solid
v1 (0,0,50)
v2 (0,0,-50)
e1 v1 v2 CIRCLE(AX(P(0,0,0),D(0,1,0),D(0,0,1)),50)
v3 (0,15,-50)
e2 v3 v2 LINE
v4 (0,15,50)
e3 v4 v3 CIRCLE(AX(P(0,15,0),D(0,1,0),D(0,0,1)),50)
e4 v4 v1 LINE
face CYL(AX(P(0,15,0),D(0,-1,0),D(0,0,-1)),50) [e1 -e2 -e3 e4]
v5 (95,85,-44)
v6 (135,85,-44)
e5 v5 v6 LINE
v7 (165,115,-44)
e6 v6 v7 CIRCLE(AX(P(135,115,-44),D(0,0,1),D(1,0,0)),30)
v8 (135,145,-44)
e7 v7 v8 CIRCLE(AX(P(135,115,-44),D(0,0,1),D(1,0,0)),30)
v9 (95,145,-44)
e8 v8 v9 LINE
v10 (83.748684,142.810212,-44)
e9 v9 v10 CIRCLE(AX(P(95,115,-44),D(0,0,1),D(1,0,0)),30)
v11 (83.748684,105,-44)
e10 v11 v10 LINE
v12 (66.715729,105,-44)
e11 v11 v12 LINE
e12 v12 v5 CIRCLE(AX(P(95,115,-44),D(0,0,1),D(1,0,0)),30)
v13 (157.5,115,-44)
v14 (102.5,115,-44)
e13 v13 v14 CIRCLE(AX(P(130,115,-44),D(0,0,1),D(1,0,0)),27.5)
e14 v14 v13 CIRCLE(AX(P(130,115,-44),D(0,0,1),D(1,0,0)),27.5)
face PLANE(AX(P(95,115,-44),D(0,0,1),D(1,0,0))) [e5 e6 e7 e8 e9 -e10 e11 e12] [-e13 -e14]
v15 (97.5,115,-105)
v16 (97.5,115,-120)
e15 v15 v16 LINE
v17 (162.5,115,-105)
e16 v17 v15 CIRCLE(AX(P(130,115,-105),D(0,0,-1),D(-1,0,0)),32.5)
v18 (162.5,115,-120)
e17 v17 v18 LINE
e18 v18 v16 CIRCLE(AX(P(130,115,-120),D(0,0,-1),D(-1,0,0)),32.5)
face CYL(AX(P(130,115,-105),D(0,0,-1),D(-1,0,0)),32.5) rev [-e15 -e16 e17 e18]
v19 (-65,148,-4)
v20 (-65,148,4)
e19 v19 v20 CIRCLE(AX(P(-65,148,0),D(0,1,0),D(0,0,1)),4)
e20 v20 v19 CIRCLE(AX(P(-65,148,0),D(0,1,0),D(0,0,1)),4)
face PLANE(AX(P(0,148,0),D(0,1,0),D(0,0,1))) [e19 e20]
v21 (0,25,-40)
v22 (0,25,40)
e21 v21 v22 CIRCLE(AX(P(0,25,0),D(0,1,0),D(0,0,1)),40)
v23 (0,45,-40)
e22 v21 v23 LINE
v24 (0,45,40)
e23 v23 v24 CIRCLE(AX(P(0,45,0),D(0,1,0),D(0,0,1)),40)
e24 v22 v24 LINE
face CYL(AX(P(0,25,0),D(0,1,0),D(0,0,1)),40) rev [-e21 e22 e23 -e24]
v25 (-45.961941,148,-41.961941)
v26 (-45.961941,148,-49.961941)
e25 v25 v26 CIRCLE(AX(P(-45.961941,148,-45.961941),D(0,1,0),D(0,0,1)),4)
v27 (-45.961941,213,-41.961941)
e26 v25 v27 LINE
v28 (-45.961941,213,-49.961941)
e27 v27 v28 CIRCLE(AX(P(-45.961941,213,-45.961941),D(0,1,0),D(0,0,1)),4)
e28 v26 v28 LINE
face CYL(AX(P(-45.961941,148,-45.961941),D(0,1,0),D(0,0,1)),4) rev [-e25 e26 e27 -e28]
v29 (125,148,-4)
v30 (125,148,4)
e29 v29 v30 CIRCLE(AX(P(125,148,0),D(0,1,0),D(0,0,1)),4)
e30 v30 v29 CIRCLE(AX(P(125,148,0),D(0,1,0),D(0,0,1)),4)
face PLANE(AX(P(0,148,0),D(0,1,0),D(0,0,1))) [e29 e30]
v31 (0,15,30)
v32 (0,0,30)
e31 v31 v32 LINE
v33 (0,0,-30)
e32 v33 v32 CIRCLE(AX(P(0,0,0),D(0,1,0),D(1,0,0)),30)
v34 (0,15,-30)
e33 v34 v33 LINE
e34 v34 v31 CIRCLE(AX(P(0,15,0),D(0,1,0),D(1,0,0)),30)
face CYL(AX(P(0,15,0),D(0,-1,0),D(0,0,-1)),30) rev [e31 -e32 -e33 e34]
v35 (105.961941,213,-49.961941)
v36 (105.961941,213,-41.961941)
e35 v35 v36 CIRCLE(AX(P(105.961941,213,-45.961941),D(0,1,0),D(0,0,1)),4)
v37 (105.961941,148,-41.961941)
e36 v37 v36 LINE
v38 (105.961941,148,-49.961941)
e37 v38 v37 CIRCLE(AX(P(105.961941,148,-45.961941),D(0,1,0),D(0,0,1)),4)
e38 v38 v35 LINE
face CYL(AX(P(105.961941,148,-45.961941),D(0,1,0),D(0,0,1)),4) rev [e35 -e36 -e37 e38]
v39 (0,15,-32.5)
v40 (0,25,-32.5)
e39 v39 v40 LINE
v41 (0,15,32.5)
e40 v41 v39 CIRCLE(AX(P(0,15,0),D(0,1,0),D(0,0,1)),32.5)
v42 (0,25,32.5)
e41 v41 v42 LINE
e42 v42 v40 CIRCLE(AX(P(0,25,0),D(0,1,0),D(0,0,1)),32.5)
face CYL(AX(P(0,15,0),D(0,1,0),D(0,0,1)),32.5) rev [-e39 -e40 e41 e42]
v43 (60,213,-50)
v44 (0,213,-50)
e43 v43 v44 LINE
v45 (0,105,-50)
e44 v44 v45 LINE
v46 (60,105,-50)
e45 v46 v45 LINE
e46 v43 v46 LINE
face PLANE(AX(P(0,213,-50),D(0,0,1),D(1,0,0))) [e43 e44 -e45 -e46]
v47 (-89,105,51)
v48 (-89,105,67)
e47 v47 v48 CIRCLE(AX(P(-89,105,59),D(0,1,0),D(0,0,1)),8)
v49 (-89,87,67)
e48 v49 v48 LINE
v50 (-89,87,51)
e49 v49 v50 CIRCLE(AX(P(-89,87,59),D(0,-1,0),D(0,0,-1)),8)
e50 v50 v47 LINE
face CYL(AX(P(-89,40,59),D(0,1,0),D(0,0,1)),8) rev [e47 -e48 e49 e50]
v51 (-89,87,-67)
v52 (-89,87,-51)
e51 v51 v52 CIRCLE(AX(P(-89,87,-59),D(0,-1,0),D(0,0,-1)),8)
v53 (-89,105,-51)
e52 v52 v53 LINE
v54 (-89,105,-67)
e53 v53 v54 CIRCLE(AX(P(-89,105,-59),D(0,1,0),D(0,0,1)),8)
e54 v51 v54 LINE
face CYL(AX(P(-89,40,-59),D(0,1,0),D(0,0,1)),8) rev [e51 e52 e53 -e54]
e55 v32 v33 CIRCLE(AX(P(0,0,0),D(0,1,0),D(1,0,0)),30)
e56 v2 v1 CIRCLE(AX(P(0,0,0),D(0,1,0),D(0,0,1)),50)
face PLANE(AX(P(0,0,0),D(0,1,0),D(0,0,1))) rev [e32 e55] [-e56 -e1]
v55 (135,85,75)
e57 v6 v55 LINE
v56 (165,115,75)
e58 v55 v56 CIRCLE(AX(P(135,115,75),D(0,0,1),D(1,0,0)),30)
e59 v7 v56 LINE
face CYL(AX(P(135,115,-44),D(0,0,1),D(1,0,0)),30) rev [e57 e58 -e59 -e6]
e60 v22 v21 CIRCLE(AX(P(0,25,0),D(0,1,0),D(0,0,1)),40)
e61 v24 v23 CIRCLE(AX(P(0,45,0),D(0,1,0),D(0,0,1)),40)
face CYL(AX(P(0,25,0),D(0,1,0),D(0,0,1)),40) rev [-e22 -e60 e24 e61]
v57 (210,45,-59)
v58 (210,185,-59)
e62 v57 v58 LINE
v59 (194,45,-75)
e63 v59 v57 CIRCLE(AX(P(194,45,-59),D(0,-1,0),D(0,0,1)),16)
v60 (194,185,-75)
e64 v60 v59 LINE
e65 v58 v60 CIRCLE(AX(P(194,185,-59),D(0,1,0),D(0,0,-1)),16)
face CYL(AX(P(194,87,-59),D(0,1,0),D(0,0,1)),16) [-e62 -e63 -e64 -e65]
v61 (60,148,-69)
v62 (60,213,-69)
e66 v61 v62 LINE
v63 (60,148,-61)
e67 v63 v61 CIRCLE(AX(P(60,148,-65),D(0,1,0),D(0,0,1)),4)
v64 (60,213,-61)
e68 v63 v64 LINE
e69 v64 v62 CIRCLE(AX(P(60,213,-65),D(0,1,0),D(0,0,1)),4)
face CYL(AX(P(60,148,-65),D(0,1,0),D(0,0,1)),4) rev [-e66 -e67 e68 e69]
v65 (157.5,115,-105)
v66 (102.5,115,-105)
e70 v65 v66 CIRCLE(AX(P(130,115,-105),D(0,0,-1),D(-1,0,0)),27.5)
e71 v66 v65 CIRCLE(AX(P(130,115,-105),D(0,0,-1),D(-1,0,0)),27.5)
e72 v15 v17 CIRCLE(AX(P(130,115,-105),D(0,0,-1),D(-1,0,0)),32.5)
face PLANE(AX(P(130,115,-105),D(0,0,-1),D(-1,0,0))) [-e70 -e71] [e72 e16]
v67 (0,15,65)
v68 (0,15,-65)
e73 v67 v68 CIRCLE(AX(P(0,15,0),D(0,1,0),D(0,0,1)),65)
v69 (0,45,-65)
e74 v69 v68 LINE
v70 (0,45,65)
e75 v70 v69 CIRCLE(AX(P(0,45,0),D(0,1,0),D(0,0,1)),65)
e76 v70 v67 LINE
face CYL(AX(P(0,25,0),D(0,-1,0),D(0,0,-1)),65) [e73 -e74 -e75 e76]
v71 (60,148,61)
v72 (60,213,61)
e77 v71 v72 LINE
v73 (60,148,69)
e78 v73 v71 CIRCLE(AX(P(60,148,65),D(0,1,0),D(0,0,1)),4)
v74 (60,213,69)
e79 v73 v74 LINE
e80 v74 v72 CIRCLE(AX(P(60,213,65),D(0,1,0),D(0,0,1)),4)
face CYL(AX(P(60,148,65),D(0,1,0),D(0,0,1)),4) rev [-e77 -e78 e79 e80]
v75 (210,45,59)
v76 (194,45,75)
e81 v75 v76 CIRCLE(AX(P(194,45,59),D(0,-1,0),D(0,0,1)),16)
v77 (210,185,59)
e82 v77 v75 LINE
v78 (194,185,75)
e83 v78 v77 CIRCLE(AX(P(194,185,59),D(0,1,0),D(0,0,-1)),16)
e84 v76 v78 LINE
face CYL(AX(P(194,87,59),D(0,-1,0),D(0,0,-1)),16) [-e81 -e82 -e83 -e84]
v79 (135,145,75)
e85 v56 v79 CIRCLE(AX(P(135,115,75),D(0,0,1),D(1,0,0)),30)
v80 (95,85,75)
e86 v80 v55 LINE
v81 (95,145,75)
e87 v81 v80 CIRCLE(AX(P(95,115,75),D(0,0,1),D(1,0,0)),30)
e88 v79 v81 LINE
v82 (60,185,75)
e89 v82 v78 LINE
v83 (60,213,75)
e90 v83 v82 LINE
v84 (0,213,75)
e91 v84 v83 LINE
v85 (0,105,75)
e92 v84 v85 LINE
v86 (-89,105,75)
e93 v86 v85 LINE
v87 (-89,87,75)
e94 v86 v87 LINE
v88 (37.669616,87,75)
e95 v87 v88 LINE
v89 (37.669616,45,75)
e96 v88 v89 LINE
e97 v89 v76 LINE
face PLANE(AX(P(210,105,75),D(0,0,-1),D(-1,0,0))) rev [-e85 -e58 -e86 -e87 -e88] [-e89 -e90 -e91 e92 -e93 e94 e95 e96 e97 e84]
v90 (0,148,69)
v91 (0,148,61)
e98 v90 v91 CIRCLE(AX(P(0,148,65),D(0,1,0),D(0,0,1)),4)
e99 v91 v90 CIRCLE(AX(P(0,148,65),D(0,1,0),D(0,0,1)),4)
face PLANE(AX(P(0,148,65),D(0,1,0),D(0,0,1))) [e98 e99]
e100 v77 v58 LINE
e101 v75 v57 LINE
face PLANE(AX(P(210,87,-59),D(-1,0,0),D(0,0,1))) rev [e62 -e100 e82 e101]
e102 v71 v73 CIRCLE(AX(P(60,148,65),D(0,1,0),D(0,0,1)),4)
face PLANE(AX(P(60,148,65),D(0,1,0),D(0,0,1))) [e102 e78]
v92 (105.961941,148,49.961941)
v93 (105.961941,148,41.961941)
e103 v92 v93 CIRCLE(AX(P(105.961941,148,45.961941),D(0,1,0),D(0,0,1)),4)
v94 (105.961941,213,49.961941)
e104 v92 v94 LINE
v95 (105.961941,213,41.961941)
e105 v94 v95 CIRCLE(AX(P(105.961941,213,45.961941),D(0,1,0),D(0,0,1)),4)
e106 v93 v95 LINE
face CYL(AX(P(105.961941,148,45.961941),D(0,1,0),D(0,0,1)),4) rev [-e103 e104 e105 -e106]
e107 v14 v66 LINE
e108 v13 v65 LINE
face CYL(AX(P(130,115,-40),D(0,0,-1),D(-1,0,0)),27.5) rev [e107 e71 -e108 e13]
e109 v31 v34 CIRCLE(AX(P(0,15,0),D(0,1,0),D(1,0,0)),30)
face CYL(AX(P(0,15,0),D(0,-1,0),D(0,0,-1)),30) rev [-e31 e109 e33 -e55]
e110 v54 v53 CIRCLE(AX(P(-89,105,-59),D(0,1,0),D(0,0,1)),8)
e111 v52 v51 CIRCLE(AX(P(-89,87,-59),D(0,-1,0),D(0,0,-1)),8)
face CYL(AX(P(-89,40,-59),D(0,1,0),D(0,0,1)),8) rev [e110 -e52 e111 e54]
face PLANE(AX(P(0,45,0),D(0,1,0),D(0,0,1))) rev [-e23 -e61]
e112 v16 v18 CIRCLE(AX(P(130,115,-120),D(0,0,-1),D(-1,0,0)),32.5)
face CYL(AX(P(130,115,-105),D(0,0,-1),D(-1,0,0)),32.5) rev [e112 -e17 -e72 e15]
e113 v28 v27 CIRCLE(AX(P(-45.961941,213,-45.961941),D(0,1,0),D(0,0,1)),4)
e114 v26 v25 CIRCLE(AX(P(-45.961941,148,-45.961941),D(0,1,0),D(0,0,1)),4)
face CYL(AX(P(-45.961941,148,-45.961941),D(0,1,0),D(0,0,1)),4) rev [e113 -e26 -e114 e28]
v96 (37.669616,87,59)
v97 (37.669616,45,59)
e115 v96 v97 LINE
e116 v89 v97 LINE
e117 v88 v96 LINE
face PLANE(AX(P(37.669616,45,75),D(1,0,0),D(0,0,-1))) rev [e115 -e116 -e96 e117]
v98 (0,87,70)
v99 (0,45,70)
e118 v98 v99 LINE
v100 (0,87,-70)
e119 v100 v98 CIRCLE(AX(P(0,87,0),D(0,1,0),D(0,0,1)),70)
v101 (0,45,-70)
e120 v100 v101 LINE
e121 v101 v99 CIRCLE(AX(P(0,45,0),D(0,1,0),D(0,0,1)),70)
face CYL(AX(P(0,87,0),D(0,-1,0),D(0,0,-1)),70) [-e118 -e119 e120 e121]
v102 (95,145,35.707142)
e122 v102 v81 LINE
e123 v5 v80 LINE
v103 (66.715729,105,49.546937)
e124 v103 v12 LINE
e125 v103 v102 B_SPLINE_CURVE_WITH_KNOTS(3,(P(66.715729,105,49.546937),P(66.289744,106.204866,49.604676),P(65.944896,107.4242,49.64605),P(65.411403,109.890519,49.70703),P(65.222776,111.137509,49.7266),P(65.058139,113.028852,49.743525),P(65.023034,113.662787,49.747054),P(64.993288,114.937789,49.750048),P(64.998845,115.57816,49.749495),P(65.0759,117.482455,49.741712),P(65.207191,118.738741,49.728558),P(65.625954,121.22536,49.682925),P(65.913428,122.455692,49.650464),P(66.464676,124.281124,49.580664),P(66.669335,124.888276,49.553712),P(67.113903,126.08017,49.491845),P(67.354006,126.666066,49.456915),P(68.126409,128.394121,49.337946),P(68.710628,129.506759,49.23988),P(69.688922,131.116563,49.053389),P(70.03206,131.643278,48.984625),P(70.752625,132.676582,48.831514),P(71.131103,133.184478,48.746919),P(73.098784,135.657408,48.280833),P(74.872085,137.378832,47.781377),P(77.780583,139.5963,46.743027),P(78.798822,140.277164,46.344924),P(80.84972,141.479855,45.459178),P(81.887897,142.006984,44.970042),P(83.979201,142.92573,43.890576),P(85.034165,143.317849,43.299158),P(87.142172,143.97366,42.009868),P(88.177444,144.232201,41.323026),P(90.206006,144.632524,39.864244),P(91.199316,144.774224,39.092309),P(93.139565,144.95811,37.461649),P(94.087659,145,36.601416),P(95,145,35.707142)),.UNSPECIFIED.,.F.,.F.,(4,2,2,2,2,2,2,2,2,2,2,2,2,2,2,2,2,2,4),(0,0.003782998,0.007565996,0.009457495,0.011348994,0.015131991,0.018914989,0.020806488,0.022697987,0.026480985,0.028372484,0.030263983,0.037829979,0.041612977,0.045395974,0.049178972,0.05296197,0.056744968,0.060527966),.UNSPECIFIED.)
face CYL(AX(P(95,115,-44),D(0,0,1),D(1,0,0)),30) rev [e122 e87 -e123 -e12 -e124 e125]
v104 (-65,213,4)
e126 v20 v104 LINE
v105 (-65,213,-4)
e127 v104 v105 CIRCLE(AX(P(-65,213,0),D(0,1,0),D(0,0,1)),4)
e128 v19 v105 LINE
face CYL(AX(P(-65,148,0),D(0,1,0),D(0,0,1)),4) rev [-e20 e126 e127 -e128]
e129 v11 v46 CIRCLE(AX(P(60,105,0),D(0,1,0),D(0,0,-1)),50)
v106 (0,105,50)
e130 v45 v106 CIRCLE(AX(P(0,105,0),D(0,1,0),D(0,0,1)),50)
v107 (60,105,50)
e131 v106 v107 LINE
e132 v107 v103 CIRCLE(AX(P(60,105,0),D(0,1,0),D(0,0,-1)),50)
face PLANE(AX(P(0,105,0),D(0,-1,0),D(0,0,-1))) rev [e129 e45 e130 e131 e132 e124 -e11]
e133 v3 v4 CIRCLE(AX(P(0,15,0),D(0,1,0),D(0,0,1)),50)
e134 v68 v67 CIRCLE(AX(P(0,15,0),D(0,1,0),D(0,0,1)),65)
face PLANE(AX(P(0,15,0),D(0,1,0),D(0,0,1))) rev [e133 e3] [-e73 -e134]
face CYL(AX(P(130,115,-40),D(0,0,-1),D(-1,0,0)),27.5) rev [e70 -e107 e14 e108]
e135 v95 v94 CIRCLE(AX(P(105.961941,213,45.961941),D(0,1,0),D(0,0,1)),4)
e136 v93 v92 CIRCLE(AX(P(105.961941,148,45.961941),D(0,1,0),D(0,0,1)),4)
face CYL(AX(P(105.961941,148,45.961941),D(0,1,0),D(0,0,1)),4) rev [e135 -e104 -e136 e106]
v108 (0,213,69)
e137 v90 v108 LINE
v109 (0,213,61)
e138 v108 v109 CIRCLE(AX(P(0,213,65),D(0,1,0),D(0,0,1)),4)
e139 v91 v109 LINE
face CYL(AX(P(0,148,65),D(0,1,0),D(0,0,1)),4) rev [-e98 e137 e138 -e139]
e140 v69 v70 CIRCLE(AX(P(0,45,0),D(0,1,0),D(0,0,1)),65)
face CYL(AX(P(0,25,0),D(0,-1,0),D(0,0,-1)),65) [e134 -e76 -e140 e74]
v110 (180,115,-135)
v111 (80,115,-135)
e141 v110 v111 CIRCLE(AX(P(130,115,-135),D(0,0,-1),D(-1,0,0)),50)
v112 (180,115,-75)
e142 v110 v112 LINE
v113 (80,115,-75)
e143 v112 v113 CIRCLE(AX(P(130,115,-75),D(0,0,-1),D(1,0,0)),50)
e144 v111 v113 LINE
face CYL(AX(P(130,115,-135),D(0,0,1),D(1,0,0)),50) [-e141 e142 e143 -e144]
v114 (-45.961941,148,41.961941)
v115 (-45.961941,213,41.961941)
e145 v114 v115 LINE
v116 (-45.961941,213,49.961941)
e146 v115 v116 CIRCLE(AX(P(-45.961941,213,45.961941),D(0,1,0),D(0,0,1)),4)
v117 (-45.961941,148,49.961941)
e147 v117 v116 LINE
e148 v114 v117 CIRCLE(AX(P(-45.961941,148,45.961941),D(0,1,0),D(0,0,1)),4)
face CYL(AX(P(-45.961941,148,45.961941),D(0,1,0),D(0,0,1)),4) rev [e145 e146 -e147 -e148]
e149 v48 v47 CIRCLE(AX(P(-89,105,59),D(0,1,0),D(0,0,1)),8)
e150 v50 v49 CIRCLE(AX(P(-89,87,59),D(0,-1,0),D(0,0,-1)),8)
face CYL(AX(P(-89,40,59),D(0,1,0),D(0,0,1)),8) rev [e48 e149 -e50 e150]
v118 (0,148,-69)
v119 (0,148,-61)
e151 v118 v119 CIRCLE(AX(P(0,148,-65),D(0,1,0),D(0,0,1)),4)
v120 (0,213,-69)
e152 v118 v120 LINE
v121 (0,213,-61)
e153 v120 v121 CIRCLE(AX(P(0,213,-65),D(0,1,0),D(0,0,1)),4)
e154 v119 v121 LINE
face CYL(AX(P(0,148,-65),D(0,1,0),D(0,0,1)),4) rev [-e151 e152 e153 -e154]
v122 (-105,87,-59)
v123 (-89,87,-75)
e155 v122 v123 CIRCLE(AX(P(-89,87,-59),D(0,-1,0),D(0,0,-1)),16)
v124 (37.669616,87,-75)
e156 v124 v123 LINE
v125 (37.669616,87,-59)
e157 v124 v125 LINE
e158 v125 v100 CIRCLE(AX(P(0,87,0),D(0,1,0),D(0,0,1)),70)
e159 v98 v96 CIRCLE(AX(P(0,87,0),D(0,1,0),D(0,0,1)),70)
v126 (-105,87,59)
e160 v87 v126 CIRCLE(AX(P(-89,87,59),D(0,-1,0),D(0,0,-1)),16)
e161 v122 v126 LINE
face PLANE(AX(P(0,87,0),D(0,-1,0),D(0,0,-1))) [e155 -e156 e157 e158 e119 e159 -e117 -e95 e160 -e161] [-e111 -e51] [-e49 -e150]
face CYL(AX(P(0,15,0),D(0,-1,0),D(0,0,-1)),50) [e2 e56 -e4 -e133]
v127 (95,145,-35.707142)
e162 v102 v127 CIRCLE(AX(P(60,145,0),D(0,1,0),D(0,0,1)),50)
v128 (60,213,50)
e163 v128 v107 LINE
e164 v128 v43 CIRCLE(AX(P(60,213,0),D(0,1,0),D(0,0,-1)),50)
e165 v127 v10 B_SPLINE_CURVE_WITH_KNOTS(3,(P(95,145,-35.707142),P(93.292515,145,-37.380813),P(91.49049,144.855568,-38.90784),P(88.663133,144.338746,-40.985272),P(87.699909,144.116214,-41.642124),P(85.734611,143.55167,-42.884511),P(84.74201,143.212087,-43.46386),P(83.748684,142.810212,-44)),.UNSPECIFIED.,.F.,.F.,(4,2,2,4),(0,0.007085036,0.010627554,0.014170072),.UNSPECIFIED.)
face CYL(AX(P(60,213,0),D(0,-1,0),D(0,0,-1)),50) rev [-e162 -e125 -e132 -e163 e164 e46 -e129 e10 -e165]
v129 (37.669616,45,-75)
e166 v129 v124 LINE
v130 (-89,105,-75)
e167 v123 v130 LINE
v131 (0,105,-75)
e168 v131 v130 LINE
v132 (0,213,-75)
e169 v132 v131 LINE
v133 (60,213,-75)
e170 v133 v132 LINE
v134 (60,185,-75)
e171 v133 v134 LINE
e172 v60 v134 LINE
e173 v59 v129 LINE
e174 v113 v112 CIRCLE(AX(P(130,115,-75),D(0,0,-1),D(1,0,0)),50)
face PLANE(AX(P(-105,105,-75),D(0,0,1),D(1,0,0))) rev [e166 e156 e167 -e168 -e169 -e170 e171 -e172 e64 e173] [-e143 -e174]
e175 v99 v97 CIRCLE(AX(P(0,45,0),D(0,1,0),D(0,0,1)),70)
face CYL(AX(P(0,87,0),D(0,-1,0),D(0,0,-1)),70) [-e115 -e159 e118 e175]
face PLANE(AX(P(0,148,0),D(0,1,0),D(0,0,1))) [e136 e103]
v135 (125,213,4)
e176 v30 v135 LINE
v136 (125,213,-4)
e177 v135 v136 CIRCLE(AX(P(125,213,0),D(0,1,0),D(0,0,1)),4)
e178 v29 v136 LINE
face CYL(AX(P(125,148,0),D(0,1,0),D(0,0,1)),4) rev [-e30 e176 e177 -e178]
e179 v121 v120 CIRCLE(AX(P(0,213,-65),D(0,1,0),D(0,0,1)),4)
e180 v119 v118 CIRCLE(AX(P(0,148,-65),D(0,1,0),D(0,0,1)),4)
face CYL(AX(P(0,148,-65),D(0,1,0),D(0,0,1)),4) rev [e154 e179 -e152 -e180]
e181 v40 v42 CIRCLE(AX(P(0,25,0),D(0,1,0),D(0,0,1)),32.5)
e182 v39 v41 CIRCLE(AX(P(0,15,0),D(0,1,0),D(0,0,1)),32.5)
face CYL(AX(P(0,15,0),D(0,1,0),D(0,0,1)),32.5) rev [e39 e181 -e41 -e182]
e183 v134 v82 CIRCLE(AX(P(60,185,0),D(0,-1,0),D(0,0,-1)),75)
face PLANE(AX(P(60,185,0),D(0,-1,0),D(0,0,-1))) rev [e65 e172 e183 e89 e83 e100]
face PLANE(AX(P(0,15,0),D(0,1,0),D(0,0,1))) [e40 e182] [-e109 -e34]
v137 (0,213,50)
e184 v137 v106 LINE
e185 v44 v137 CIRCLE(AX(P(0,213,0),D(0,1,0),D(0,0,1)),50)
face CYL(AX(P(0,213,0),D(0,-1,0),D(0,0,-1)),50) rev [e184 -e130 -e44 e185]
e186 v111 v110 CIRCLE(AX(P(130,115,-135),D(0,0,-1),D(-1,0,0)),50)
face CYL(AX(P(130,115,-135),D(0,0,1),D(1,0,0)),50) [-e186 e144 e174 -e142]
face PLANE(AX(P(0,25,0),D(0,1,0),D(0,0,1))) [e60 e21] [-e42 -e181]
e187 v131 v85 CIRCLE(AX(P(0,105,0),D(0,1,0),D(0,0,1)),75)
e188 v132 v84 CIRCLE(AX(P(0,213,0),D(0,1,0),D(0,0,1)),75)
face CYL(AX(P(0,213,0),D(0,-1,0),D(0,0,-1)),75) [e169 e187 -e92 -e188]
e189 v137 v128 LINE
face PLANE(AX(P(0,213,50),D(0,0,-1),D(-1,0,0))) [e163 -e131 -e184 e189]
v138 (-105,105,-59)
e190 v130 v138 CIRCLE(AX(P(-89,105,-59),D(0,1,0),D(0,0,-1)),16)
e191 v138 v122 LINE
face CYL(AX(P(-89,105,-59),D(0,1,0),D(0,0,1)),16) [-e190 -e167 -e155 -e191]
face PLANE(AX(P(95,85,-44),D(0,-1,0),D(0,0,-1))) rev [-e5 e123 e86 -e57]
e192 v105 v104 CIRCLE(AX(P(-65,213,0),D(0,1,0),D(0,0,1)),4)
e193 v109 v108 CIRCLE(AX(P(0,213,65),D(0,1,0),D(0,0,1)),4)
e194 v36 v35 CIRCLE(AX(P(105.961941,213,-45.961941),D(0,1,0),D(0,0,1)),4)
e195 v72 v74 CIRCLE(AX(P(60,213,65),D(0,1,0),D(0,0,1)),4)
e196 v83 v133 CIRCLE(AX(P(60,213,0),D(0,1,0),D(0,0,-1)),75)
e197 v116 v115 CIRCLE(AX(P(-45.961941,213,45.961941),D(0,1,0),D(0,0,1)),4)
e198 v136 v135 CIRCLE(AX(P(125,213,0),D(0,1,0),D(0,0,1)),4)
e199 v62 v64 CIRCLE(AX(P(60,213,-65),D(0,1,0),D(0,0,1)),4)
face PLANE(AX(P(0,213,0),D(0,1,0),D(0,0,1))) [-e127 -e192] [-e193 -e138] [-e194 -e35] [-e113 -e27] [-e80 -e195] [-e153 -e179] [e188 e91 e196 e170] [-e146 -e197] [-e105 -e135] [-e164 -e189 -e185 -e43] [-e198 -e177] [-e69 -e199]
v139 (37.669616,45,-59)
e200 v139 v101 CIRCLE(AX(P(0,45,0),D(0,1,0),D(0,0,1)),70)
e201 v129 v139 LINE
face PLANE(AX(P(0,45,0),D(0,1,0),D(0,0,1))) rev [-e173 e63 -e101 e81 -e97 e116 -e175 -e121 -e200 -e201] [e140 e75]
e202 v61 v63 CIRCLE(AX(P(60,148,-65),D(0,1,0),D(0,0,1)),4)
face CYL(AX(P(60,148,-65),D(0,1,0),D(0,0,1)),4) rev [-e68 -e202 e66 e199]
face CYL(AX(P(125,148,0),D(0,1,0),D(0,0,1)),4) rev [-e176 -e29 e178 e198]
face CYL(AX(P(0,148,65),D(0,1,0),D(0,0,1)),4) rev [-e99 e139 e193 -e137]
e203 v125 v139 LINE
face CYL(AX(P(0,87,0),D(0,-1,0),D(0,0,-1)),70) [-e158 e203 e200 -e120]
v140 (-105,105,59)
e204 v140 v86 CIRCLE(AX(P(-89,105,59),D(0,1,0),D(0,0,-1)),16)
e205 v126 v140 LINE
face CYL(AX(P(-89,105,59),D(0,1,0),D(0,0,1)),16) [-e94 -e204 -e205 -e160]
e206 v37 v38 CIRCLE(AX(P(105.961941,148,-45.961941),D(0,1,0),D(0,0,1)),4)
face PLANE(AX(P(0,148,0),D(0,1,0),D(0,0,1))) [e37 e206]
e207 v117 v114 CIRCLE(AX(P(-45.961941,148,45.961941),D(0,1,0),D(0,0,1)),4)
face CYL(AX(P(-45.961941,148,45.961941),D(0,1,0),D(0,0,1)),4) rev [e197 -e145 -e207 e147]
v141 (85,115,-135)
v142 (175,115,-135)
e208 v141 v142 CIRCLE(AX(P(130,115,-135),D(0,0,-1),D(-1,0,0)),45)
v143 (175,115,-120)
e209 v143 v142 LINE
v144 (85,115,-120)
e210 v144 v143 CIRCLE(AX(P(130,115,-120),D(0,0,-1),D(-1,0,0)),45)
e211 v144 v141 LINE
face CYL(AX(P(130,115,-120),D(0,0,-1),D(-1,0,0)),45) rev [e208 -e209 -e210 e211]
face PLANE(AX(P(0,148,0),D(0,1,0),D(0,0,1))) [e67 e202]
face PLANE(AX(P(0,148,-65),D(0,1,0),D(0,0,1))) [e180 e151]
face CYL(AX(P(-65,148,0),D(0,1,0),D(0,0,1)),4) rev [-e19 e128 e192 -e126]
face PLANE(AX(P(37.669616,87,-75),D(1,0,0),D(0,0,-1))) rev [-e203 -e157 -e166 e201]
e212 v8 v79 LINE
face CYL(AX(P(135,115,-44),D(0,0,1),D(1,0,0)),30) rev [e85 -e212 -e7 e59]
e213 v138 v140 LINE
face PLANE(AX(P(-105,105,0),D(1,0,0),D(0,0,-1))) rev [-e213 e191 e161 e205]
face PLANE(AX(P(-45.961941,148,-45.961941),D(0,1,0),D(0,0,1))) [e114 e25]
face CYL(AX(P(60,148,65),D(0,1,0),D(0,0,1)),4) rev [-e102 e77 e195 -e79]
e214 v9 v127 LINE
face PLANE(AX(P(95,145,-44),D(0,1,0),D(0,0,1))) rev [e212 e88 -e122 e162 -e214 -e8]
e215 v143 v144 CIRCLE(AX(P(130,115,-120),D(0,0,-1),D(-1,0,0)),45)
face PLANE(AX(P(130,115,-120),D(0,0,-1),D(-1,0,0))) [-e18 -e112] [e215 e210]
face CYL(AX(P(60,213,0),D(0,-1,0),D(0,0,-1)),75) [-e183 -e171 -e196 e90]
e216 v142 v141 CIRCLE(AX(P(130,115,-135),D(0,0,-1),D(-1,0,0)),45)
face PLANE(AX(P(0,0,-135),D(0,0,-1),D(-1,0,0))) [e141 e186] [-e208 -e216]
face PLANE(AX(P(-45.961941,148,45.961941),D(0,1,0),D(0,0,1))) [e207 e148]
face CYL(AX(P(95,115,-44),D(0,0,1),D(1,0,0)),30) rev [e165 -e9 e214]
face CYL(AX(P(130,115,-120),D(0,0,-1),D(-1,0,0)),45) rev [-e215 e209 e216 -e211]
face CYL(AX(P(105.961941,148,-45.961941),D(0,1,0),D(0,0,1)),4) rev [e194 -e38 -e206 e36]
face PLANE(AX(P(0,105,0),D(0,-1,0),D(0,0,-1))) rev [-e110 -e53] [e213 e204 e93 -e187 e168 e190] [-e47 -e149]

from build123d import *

# Parameters (mm, degrees)
BASE_TUBE_SKETCH_R                 = 50
BASE_TUBE_SKETCH_R_2               = 30
BASE_TUBE_DEPTH                    = 15
LOWER_FLANGE_SKETCH_R              = 65
LOWER_FLANGE_DEPTH                 = 10
LOWER_FLANGE_BORE_SKETCH_R         = 32.5
LOWER_FLANGE_BORE_DEPTH            = 10
SPIGOT_SKETCH_R                    = 65
SPIGOT_DEPTH                       = 20
SPIGOT_BORE_SKETCH_R               = 40
SPIGOT_BORE_DEPTH                  = 20
LOWER_BLOCK_DEPTH                  = 42
MOUNTING_LUG_DEPTH                 = 18
MAIN_BODY_DEPTH                    = 108
BODY_EXTENSION_DEPTH               = 80
INFILL_BLOCK_A_SKETCH_W            = 172.330383596
INFILL_BLOCK_A_SKETCH_H            = 42
INFILL_BLOCK_A_DEPTH               = 16
THROUGH_SLOT_DEPTH                 = 119
INFILL_BLOCK_B_SKETCH_W            = 172.330383596
INFILL_BLOCK_B_SKETCH_H            = 42
INFILL_BLOCK_B_DEPTH               = 16
SIDE_PORT_BOSS_SKETCH_R            = 50
SIDE_PORT_BOSS_DEPTH               = 60
PORT_COUNTERBORE_SKETCH_R          = 45
PORT_COUNTERBORE_DEPTH             = 15
PORT_STEP_BORE_SKETCH_R            = 32.5
PORT_STEP_BORE_DEPTH               = 15
PORT_THROUGH_BORE_SKETCH_R         = 27.5
PORT_THROUGH_BORE_DEPTH            = 65
BLOCK_EDGE_FILLET_R16_A_R          = 16
BLOCK_EDGE_FILLET_R16_B_R          = 16
LUG_EDGE_FILLET_R16_A_R            = 16
LUG_EDGE_FILLET_R16_B_R            = 16
LUG_POCKET_SKETCH_R                = 8
LUG_POCKET_DEPTH                   = 65
TOP_CAVITY_AND_BOLT_HOLES_SKETCH_R = 4
TOP_CAVITY_AND_BOLT_HOLES_DEPTH    = 65


with BuildPart() as part:
    # Base Tube Sketch → Base Tube (new body)
    with BuildSketch(Plane(origin=(0, 0, 0), x_dir=(1, 0, 0), z_dir=(0, 1, 0))):
        Circle(BASE_TUBE_SKETCH_R)
        Circle(BASE_TUBE_SKETCH_R_2, mode=Mode.SUBTRACT)
    extrude(amount=BASE_TUBE_DEPTH)

    # Lower Flange Sketch → Lower Flange (add)
    with BuildSketch(Plane(origin=(0, 15, 0), x_dir=(1, 0, 0), z_dir=(0, 1, 0))):
        with Locations(Location((0, 0, 0), (0, 0, 270))):
            Circle(LOWER_FLANGE_SKETCH_R)
    extrude(amount=LOWER_FLANGE_DEPTH)

    # Lower Flange Bore Sketch → Lower Flange Bore (cut)
    with BuildSketch(Plane(origin=(0, 25, 0), x_dir=(1, 0, 0), z_dir=(0, 1, 0))):
        with Locations(Location((0, 0, 0), (0, 0, 270))):
            Circle(LOWER_FLANGE_BORE_SKETCH_R)
    extrude(amount=-LOWER_FLANGE_BORE_DEPTH, mode=Mode.SUBTRACT)

    # Spigot Sketch → Spigot (add)
    with BuildSketch(Plane(origin=(0, 25, 0), x_dir=(1, 0, 0), z_dir=(0, 1, 0))):
        with Locations(Location((0, 0, 0), (0, 0, 270))):
            Circle(SPIGOT_SKETCH_R)
    extrude(amount=SPIGOT_DEPTH)

    # Spigot Bore Sketch → Spigot Bore (cut)
    with BuildSketch(Plane(origin=(0, 45, 0), x_dir=(1, 0, 0), z_dir=(0, 1, 0))):
        with Locations(Location((0, 0, 0), (0, 0, 270))):
            Circle(SPIGOT_BORE_SKETCH_R)
    extrude(amount=-SPIGOT_BORE_DEPTH, mode=Mode.SUBTRACT)

    # Lower Block Sketch → Lower Block (add)
    with BuildSketch(Plane(origin=(0, 45, 0), x_dir=(1, 0, 0), z_dir=(0, 1, 0))):
        with BuildLine():
            Line((37.669616404, 59), (210, 59))
            Line((210, 59), (210, -59))
            Line((210, -59), (37.669616404, -59))
            ThreePointArc((37.669616404, -59), (-70, 0), (37.669616404, 59))
        make_face()
    extrude(amount=LOWER_BLOCK_DEPTH)

    # Mounting Lug Sketch → Mounting Lug (add)
    with BuildSketch(Plane(origin=(0, 87, 0), x_dir=(1, 0, 0), z_dir=(0, 1, 0))):
        Polygon((-105, 0), (-105, 75), (210, 75), (210, -75), (-105, -75), align=None)
    extrude(amount=MOUNTING_LUG_DEPTH)

    # Main Body Sketch → Main Body (add)
    with BuildSketch(Plane(origin=(0, 105, 0), x_dir=(1, 0, 0), z_dir=(0, 1, 0))):
        with BuildLine():
            Line((0, 75), (60, 75))
            ThreePointArc((60, 75), (135, 0), (60, -75))
            Line((60, -75), (0, -75))
            ThreePointArc((0, -75), (-75, 0), (0, 75))
        make_face()
        with BuildLine():
            Line((0, 50), (60, 50))
            ThreePointArc((60, 50), (110, 0), (60, -50))
            Line((60, -50), (0, -50))
            ThreePointArc((0, -50), (-50, 0), (0, 50))
        make_face(mode=Mode.SUBTRACT)
    extrude(amount=MAIN_BODY_DEPTH)

    # Body Extension Sketch → Body Extension (add)
    with BuildSketch(Plane(origin=(0, 105, 0), x_dir=(1, 0, 0), z_dir=(0, 1, 0))):
        with BuildLine():
            Line((60, 75), (210, 75))
            Line((210, 75), (210, -75))
            Line((210, -75), (60, -75))
            ThreePointArc((60, -75), (135, 0), (60, 75))
        make_face()
    extrude(amount=BODY_EXTENSION_DEPTH)

    # Infill Block A Sketch → Infill Block A (add)
    with BuildSketch(Plane.XY.offset(59)):
        with Locations((123.834808202, 66)):
            Rectangle(INFILL_BLOCK_A_SKETCH_W, INFILL_BLOCK_A_SKETCH_H)
    extrude(amount=INFILL_BLOCK_A_DEPTH)

    # Through Slot Sketch → Through Slot (cut)
    with BuildSketch(Plane.XY.offset(75)):
        with BuildLine():
            Line((95, 145), (135, 145))
            ThreePointArc((135, 145), (165, 115), (135, 85))
            Line((135, 85), (95, 85))
            ThreePointArc((95, 85), (65, 115), (95, 145))
        make_face()
    extrude(amount=-THROUGH_SLOT_DEPTH, mode=Mode.SUBTRACT)

    # Infill Block B Sketch → Infill Block B (add)
    with BuildSketch(Plane(origin=(0, 0, -59), x_dir=(-1, 0, 0), z_dir=(0, 0, -1))):
        with Locations((-123.834808202, 66)):
            Rectangle(INFILL_BLOCK_B_SKETCH_W, INFILL_BLOCK_B_SKETCH_H)
    extrude(amount=INFILL_BLOCK_B_DEPTH)

    # Side Port Boss Sketch → Side Port Boss (add)
    with BuildSketch(Plane(origin=(0, 0, -75), x_dir=(-1, 0, 0), z_dir=(0, 0, -1))):
        with Locations(Location((-130, 115, 0), (0, 0, 180))):
            Circle(SIDE_PORT_BOSS_SKETCH_R)
    extrude(amount=SIDE_PORT_BOSS_DEPTH)

    # Port Counterbore Sketch → Port Counterbore (cut)
    with BuildSketch(Plane(origin=(0, 0, -135), x_dir=(-1, 0, 0), z_dir=(0, 0, -1))):
        with Locations((-130, 115)):
            Circle(PORT_COUNTERBORE_SKETCH_R)
    extrude(amount=-PORT_COUNTERBORE_DEPTH, mode=Mode.SUBTRACT)

    # Port Step Bore Sketch → Port Step Bore (cut)
    with BuildSketch(Plane(origin=(0, 0, -120), x_dir=(-1, 0, 0), z_dir=(0, 0, -1))):
        with Locations((-130, 115)):
            Circle(PORT_STEP_BORE_SKETCH_R)
    extrude(amount=-PORT_STEP_BORE_DEPTH, mode=Mode.SUBTRACT)

    # Port Through Bore Sketch → Port Through Bore (cut)
    with BuildSketch(Plane(origin=(0, 0, -105), x_dir=(-1, 0, 0), z_dir=(0, 0, -1))):
        with Locations((-130, 115)):
            Circle(PORT_THROUGH_BORE_SKETCH_R)
    extrude(amount=-PORT_THROUGH_BORE_DEPTH, mode=Mode.SUBTRACT)

    # Block Edge Fillet R16 A
    block_edge_fillet_r16_a_edges = [part.edges().sort_by_distance(p)[0] for p in [
        (210, 115, 75),
    ]]
    fillet(block_edge_fillet_r16_a_edges, radius=BLOCK_EDGE_FILLET_R16_A_R)

    # Block Edge Fillet R16 B
    block_edge_fillet_r16_b_edges = [part.edges().sort_by_distance(p)[0] for p in [
        (210, 115, -75),
    ]]
    fillet(block_edge_fillet_r16_b_edges, radius=BLOCK_EDGE_FILLET_R16_B_R)

    # Lug Edge Fillet R16 A
    lug_edge_fillet_r16_a_edges = [part.edges().sort_by_distance(p)[0] for p in [
        (-105, 96, 75),
    ]]
    fillet(lug_edge_fillet_r16_a_edges, radius=LUG_EDGE_FILLET_R16_A_R)

    # Lug Edge Fillet R16 B
    lug_edge_fillet_r16_b_edges = [part.edges().sort_by_distance(p)[0] for p in [
        (-105, 96, -75),
    ]]
    fillet(lug_edge_fillet_r16_b_edges, radius=LUG_EDGE_FILLET_R16_B_R)

    # Lug Pocket Sketch → Lug Pocket (cut)
    with BuildSketch(Plane(origin=(0, 105, 0), x_dir=(1, 0, 0), z_dir=(0, 1, 0))):
        with Locations(Location((-89, 59, 0), (0, 0, 270))):
            Circle(LUG_POCKET_SKETCH_R)
        with Locations(Location((-89, -59, 0), (0, 0, 270))):
            Circle(LUG_POCKET_SKETCH_R)
    extrude(amount=-LUG_POCKET_DEPTH, mode=Mode.SUBTRACT)

    # Top Cavity and Bolt Holes Sketch → Top Cavity and Bolt Holes (cut)
    with BuildSketch(Plane(origin=(0, 213, 0), x_dir=(1, 0, 0), z_dir=(0, 1, 0))):
        with Locations(Location((-65, 0, 0), (0, 0, 270))):
            Circle(TOP_CAVITY_AND_BOLT_HOLES_SKETCH_R)
        with Locations(Location((60, 65, 0), (0, 0, 270))):
            Circle(TOP_CAVITY_AND_BOLT_HOLES_SKETCH_R)
        with Locations(Location((105.961940777, 45.961940777, 0), (0, 0, 270))):
            Circle(TOP_CAVITY_AND_BOLT_HOLES_SKETCH_R)
        with Locations(Location((125, 0, 0), (0, 0, 270))):
            Circle(TOP_CAVITY_AND_BOLT_HOLES_SKETCH_R)
        with Locations(Location((105.961940777, -45.961940777, 0), (0, 0, 270))):
            Circle(TOP_CAVITY_AND_BOLT_HOLES_SKETCH_R)
        with Locations(Location((-45.961940777, -45.961940777, 0), (0, 0, 270))):
            Circle(TOP_CAVITY_AND_BOLT_HOLES_SKETCH_R)
        with Locations(Location((-45.961940777, 45.961940777, 0), (0, 0, 270))):
            Circle(TOP_CAVITY_AND_BOLT_HOLES_SKETCH_R)
        with Locations(Location((0, 65, 0), (0, 0, 270))):
            Circle(TOP_CAVITY_AND_BOLT_HOLES_SKETCH_R)
        with Locations(Location((60, -65, 0), (0, 0, 270))):
            Circle(TOP_CAVITY_AND_BOLT_HOLES_SKETCH_R)
        with Locations(Location((0, -65, 0), (0, 0, 270))):
            Circle(TOP_CAVITY_AND_BOLT_HOLES_SKETCH_R)
    extrude(amount=-TOP_CAVITY_AND_BOLT_HOLES_DEPTH, mode=Mode.SUBTRACT)


solid = part.part
